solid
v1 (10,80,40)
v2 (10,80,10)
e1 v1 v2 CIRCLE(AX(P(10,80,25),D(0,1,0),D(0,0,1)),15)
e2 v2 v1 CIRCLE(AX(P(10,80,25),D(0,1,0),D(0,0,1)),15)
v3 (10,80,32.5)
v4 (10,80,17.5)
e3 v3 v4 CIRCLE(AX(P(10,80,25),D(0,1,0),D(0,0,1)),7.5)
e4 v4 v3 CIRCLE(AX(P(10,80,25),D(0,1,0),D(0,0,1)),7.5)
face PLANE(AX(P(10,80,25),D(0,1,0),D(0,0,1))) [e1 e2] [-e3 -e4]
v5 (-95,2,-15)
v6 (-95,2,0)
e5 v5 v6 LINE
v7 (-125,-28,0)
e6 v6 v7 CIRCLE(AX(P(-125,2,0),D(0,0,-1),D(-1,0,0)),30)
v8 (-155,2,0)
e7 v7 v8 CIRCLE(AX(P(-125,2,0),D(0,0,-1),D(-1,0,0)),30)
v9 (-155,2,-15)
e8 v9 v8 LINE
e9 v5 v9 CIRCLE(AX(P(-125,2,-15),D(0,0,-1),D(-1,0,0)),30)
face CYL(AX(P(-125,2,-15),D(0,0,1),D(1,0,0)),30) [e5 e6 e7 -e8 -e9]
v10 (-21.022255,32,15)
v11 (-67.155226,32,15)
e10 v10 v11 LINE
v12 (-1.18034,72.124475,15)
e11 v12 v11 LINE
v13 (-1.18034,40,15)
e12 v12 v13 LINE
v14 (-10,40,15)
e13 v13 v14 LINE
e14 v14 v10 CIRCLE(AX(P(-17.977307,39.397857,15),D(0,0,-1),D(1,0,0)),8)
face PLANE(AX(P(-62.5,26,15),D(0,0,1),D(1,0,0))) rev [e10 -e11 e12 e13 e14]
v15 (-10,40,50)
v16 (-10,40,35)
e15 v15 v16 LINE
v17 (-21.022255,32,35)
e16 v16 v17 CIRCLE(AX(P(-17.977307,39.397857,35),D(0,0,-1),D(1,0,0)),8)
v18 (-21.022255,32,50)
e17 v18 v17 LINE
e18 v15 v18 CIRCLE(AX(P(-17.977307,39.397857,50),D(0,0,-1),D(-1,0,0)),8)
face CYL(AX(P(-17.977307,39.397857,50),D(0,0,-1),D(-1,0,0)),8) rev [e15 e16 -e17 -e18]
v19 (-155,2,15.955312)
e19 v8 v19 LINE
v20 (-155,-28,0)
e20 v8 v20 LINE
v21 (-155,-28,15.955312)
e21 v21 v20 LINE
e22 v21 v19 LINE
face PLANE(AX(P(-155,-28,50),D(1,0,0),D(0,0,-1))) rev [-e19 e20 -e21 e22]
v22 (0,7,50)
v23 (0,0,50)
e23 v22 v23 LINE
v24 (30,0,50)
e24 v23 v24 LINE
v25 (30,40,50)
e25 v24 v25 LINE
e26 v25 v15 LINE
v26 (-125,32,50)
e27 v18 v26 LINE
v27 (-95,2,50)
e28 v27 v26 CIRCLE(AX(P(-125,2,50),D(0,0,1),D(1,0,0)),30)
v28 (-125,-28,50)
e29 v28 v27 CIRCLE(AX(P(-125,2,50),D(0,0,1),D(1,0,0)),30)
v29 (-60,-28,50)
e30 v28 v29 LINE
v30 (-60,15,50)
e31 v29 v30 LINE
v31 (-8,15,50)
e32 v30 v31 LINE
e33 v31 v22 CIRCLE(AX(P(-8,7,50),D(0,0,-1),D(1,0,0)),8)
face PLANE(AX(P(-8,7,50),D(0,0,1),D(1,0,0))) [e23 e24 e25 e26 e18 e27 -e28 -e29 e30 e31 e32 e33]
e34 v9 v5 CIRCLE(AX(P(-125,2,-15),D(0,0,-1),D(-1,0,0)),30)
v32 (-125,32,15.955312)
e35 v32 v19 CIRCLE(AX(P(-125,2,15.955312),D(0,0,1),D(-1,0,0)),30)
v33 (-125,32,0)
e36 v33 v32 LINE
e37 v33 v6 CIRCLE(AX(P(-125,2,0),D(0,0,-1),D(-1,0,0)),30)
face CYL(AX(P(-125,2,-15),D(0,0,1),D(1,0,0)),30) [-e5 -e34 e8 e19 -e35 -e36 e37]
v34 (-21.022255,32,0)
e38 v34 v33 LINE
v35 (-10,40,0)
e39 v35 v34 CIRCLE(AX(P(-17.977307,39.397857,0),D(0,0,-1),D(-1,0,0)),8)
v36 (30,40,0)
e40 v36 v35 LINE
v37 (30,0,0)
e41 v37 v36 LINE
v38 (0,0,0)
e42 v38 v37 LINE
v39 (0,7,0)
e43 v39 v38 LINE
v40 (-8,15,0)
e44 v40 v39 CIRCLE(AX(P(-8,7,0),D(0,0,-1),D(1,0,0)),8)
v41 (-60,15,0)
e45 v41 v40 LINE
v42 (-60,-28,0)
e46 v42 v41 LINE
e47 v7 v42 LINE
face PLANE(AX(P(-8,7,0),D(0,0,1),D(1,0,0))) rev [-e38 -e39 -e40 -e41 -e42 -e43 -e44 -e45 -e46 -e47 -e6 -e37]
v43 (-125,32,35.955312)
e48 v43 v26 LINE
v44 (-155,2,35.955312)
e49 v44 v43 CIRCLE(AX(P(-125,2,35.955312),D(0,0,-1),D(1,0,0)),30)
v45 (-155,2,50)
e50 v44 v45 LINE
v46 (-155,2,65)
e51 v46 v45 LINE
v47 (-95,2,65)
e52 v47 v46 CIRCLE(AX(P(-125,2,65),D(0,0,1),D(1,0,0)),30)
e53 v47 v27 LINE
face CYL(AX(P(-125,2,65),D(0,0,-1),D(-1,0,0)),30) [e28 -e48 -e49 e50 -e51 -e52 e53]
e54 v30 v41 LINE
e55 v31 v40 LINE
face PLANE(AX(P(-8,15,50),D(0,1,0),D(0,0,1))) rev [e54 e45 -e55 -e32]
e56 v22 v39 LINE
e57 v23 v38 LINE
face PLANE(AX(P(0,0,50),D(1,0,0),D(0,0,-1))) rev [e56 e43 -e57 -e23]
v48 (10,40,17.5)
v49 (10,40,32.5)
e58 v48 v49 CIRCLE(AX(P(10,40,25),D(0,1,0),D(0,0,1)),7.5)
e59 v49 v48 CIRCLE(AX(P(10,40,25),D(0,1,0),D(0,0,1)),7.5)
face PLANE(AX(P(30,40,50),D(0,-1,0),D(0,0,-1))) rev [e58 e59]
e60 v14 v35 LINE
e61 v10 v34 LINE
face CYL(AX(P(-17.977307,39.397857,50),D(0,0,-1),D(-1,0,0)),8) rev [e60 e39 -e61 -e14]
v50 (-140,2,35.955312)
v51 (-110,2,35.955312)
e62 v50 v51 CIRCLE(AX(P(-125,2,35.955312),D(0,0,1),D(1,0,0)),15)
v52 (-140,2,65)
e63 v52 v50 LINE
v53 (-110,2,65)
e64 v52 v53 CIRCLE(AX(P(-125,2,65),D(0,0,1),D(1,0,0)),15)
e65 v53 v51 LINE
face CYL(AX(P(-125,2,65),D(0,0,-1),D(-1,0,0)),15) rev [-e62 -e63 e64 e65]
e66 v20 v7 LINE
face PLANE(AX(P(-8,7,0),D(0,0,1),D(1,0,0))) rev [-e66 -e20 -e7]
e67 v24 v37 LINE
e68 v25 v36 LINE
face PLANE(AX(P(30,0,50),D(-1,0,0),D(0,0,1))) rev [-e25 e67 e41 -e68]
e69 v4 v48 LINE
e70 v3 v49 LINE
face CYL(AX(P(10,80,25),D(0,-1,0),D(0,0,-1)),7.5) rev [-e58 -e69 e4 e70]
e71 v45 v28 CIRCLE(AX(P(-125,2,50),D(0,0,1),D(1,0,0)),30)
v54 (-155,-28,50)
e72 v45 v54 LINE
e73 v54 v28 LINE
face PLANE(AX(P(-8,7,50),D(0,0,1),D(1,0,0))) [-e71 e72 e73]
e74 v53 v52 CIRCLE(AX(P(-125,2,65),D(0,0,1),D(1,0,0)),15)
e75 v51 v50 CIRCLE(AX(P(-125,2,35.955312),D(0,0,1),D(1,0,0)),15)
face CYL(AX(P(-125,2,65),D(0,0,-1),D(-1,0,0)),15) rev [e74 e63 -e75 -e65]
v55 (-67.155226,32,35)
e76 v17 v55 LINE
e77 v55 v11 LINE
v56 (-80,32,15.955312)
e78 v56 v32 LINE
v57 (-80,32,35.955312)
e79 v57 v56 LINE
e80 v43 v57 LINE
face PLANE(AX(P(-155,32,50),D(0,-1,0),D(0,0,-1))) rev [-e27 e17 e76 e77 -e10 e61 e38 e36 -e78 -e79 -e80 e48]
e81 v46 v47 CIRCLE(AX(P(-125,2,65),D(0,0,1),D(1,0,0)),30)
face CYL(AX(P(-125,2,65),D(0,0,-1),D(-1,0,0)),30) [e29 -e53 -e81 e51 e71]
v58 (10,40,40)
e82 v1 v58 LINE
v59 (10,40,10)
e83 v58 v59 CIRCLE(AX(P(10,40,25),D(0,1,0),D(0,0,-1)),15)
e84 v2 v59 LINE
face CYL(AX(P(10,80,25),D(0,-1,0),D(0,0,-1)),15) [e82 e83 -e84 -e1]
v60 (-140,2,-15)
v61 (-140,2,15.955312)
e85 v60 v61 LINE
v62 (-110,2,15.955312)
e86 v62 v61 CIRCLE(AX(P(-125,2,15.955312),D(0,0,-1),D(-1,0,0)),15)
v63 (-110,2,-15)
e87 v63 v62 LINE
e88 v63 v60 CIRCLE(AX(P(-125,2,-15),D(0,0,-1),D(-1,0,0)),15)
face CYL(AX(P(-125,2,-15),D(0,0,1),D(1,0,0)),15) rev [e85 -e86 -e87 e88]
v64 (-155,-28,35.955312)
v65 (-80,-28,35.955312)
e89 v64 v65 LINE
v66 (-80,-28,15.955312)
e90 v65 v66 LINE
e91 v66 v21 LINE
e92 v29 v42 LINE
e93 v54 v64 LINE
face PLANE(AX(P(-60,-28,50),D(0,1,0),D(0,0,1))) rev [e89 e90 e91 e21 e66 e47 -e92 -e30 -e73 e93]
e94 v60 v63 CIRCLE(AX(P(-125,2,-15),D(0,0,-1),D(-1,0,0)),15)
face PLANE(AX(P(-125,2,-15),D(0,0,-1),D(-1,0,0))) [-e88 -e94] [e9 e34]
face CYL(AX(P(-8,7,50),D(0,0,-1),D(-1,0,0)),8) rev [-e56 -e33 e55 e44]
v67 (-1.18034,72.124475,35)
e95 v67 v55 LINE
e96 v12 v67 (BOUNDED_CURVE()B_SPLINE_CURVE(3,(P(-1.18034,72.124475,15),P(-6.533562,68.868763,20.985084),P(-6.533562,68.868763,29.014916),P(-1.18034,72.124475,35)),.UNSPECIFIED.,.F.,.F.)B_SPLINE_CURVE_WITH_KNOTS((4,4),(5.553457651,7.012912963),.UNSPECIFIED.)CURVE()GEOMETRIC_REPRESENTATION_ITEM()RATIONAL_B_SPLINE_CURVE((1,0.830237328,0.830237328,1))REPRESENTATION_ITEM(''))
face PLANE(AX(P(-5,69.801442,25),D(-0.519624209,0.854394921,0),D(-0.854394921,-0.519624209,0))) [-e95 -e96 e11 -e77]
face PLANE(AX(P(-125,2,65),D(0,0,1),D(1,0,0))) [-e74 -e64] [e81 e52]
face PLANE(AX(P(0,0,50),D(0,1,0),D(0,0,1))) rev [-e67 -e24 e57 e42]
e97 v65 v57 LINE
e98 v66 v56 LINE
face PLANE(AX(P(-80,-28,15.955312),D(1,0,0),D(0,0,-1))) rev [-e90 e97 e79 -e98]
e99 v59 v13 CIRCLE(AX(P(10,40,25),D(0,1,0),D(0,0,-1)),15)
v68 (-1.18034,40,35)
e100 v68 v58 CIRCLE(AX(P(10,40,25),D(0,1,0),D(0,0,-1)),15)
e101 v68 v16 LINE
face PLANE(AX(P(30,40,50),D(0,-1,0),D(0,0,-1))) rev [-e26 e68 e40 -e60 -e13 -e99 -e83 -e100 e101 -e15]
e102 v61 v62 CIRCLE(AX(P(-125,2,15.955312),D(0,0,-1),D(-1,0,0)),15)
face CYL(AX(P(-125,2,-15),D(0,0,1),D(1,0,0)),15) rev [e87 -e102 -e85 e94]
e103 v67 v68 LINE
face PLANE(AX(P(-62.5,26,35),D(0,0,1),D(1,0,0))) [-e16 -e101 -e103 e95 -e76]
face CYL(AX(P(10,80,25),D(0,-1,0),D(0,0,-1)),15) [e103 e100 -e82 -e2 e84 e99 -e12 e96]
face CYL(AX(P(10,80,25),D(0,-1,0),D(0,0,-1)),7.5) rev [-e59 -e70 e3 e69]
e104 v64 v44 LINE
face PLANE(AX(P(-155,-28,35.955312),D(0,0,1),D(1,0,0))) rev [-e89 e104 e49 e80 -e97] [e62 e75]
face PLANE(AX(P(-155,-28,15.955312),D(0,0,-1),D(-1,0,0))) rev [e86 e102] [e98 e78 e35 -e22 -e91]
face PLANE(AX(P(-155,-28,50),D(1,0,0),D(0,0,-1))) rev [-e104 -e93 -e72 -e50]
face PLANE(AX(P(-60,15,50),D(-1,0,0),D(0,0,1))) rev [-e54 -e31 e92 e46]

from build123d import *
from build123d.topology import SkipClean

# Parameters (mm, degrees)
ARM_BODY_DEPTH            = 50
FRONT_LUG_SKETCH_R        = 30
FRONT_LUG_SKETCH_R_2      = 15
FRONT_LUG_30_DEPTH        = 15
REAR_START                = 15
REAR_LUG_SKETCH_R         = 30
REAR_LUG_SKETCH_R_2       = 15
REAR_LUG_30_DEPTH         = 15
TOP_SLOT_SKETCH_W         = 75
TOP_SLOT_SKETCH_H         = 20
TOP_SLOT_CUT_DEPTH        = 179.465683
LUG_RELIEF_CUT_DEPTH      = 173.771525
PIN_POST_SKETCH_R         = 15
PIN_POST_SKETCH_R_2       = 7.5
PIN_POST_15_DEPTH         = 40
SUPPORT_RIB_REACH         = 180.955
SUPPORT_RIB_SKETCH_WALL_W = 432.658256
SUPPORT_RIB_SKETCH_WALL_H = 20
EYE_BORE_SKETCH_R         = 15
EYE_BORE_DEPTH            = 187.145105


with BuildPart() as part:
    # Arm Profile Sketch → Arm Body (new body)
    with BuildSketch(Plane.XY):
        with BuildLine():
            Line((0, 0), (30, 0))
            Line((30, 0), (30, 40))
            Line((30, 40), (-10, 40))
            ThreePointArc((-10, 40), (-13.278154, 32.923449), (-21.022255, 32))
            Line((-21.022255, 32), (-155, 32))
            Line((-155, 32), (-155, -28))
            Line((-155, -28), (-60, -28))
            Line((-60, -28), (-60, 15))
            Line((-60, 15), (-8, 15))
            ThreePointArc((-8, 15), (-2.343146, 12.656854), (0, 7))
            Line((0, 7), (0, 0))
        make_face()
    extrude(amount=ARM_BODY_DEPTH)

    # Front Lug Sketch → Front Lug Ø30 (add)
    with BuildSketch(Plane.XY.offset(50)):
        with Locations(Location((-125, 2, 0), (0, 0, 180))):
            Circle(FRONT_LUG_SKETCH_R)
        with Locations((-125, 2)):
            Circle(FRONT_LUG_SKETCH_R_2, mode=Mode.SUBTRACT)
    extrude(amount=FRONT_LUG_30_DEPTH)

    # Rear Lug Sketch → Rear Lug Ø30 (add)
    with BuildSketch(Plane(origin=(0, 0, 0), x_dir=(-1, 0, 0), z_dir=(0, 0, -1)).offset(REAR_START)):
        with Locations((125, 2)):
            Circle(REAR_LUG_SKETCH_R)
        with Locations(Location((125, 2, 0), (0, 0, 180))):
            Circle(REAR_LUG_SKETCH_R_2, mode=Mode.SUBTRACT)
    extrude(amount=-REAR_LUG_30_DEPTH)

    # Top Slot Sketch → Top Slot Cut (cut, through all)
    with BuildSketch(Plane(origin=(0, 32, 0), x_dir=(1, 0, 0), z_dir=(0, 1, 0))):
        with Locations((-117.5, -25.955312)):
            Rectangle(TOP_SLOT_SKETCH_W, TOP_SLOT_SKETCH_H)
    extrude(amount=-TOP_SLOT_CUT_DEPTH, mode=Mode.SUBTRACT)

    # Lug Relief Sketch → Lug Relief Cut (cut, through all)
    with SkipClean():  # the faces are left unmerged after this step: merging them gives an invalid solid
        with BuildSketch(Plane.XY.offset(50)):
            with BuildLine():
                Line((-155, 32), (-125, 32))
                ThreePointArc((-125, 32), (-146.213203, 23.213203), (-155, 2))
                Line((-155, 2), (-155, 32))
            make_face()
        extrude(amount=-LUG_RELIEF_CUT_DEPTH, mode=Mode.SUBTRACT)

    # Pin Post Sketch → Pin Post Ø15 (add)
    with SkipClean():  # the faces are left unmerged after this step: merging them gives an invalid solid
        with BuildSketch(Plane(origin=(0, 40, 0), x_dir=(1, 0, 0), z_dir=(0, 1, 0))):
            with Locations(Location((10, -25, 0), (0, 0, 90))):
                Circle(PIN_POST_SKETCH_R)
            with Locations(Location((10, -25, 0), (0, 0, 270))):
                Circle(PIN_POST_SKETCH_R_2, mode=Mode.SUBTRACT)
        extrude(amount=PIN_POST_15_DEPTH)

    # Support Rib Sketch wall → Support Rib (add, up to next)
    with BuildSketch(Plane(origin=(-36.077613, 50.900721, 25), x_dir=(-0.854394921364, -0.519624208778, 0), z_dir=(0.519624208778, -0.854394921364, 0)), mode=Mode.PRIVATE) as support_rib_sk1:
        Rectangle(SUPPORT_RIB_SKETCH_WALL_W, SUPPORT_RIB_SKETCH_WALL_H)
    support_rib_tool1 = extrude(support_rib_sk1.sketch, amount=SUPPORT_RIB_REACH, mode=Mode.PRIVATE) - part.part
    add(support_rib_tool1.solids().sort_by_distance((-36.077613, 50.900721, 25))[0])

    # Eye Bore Sketch → Eye Bore (cut, through all)
    with SkipClean():  # the faces are left unmerged after this step: merging them gives an invalid solid
        with BuildSketch(Plane.XY.offset(50)):
            with Locations((-125, 2)):
                Circle(EYE_BORE_SKETCH_R)
        extrude(amount=-EYE_BORE_DEPTH, mode=Mode.SUBTRACT)


solid = part.part
